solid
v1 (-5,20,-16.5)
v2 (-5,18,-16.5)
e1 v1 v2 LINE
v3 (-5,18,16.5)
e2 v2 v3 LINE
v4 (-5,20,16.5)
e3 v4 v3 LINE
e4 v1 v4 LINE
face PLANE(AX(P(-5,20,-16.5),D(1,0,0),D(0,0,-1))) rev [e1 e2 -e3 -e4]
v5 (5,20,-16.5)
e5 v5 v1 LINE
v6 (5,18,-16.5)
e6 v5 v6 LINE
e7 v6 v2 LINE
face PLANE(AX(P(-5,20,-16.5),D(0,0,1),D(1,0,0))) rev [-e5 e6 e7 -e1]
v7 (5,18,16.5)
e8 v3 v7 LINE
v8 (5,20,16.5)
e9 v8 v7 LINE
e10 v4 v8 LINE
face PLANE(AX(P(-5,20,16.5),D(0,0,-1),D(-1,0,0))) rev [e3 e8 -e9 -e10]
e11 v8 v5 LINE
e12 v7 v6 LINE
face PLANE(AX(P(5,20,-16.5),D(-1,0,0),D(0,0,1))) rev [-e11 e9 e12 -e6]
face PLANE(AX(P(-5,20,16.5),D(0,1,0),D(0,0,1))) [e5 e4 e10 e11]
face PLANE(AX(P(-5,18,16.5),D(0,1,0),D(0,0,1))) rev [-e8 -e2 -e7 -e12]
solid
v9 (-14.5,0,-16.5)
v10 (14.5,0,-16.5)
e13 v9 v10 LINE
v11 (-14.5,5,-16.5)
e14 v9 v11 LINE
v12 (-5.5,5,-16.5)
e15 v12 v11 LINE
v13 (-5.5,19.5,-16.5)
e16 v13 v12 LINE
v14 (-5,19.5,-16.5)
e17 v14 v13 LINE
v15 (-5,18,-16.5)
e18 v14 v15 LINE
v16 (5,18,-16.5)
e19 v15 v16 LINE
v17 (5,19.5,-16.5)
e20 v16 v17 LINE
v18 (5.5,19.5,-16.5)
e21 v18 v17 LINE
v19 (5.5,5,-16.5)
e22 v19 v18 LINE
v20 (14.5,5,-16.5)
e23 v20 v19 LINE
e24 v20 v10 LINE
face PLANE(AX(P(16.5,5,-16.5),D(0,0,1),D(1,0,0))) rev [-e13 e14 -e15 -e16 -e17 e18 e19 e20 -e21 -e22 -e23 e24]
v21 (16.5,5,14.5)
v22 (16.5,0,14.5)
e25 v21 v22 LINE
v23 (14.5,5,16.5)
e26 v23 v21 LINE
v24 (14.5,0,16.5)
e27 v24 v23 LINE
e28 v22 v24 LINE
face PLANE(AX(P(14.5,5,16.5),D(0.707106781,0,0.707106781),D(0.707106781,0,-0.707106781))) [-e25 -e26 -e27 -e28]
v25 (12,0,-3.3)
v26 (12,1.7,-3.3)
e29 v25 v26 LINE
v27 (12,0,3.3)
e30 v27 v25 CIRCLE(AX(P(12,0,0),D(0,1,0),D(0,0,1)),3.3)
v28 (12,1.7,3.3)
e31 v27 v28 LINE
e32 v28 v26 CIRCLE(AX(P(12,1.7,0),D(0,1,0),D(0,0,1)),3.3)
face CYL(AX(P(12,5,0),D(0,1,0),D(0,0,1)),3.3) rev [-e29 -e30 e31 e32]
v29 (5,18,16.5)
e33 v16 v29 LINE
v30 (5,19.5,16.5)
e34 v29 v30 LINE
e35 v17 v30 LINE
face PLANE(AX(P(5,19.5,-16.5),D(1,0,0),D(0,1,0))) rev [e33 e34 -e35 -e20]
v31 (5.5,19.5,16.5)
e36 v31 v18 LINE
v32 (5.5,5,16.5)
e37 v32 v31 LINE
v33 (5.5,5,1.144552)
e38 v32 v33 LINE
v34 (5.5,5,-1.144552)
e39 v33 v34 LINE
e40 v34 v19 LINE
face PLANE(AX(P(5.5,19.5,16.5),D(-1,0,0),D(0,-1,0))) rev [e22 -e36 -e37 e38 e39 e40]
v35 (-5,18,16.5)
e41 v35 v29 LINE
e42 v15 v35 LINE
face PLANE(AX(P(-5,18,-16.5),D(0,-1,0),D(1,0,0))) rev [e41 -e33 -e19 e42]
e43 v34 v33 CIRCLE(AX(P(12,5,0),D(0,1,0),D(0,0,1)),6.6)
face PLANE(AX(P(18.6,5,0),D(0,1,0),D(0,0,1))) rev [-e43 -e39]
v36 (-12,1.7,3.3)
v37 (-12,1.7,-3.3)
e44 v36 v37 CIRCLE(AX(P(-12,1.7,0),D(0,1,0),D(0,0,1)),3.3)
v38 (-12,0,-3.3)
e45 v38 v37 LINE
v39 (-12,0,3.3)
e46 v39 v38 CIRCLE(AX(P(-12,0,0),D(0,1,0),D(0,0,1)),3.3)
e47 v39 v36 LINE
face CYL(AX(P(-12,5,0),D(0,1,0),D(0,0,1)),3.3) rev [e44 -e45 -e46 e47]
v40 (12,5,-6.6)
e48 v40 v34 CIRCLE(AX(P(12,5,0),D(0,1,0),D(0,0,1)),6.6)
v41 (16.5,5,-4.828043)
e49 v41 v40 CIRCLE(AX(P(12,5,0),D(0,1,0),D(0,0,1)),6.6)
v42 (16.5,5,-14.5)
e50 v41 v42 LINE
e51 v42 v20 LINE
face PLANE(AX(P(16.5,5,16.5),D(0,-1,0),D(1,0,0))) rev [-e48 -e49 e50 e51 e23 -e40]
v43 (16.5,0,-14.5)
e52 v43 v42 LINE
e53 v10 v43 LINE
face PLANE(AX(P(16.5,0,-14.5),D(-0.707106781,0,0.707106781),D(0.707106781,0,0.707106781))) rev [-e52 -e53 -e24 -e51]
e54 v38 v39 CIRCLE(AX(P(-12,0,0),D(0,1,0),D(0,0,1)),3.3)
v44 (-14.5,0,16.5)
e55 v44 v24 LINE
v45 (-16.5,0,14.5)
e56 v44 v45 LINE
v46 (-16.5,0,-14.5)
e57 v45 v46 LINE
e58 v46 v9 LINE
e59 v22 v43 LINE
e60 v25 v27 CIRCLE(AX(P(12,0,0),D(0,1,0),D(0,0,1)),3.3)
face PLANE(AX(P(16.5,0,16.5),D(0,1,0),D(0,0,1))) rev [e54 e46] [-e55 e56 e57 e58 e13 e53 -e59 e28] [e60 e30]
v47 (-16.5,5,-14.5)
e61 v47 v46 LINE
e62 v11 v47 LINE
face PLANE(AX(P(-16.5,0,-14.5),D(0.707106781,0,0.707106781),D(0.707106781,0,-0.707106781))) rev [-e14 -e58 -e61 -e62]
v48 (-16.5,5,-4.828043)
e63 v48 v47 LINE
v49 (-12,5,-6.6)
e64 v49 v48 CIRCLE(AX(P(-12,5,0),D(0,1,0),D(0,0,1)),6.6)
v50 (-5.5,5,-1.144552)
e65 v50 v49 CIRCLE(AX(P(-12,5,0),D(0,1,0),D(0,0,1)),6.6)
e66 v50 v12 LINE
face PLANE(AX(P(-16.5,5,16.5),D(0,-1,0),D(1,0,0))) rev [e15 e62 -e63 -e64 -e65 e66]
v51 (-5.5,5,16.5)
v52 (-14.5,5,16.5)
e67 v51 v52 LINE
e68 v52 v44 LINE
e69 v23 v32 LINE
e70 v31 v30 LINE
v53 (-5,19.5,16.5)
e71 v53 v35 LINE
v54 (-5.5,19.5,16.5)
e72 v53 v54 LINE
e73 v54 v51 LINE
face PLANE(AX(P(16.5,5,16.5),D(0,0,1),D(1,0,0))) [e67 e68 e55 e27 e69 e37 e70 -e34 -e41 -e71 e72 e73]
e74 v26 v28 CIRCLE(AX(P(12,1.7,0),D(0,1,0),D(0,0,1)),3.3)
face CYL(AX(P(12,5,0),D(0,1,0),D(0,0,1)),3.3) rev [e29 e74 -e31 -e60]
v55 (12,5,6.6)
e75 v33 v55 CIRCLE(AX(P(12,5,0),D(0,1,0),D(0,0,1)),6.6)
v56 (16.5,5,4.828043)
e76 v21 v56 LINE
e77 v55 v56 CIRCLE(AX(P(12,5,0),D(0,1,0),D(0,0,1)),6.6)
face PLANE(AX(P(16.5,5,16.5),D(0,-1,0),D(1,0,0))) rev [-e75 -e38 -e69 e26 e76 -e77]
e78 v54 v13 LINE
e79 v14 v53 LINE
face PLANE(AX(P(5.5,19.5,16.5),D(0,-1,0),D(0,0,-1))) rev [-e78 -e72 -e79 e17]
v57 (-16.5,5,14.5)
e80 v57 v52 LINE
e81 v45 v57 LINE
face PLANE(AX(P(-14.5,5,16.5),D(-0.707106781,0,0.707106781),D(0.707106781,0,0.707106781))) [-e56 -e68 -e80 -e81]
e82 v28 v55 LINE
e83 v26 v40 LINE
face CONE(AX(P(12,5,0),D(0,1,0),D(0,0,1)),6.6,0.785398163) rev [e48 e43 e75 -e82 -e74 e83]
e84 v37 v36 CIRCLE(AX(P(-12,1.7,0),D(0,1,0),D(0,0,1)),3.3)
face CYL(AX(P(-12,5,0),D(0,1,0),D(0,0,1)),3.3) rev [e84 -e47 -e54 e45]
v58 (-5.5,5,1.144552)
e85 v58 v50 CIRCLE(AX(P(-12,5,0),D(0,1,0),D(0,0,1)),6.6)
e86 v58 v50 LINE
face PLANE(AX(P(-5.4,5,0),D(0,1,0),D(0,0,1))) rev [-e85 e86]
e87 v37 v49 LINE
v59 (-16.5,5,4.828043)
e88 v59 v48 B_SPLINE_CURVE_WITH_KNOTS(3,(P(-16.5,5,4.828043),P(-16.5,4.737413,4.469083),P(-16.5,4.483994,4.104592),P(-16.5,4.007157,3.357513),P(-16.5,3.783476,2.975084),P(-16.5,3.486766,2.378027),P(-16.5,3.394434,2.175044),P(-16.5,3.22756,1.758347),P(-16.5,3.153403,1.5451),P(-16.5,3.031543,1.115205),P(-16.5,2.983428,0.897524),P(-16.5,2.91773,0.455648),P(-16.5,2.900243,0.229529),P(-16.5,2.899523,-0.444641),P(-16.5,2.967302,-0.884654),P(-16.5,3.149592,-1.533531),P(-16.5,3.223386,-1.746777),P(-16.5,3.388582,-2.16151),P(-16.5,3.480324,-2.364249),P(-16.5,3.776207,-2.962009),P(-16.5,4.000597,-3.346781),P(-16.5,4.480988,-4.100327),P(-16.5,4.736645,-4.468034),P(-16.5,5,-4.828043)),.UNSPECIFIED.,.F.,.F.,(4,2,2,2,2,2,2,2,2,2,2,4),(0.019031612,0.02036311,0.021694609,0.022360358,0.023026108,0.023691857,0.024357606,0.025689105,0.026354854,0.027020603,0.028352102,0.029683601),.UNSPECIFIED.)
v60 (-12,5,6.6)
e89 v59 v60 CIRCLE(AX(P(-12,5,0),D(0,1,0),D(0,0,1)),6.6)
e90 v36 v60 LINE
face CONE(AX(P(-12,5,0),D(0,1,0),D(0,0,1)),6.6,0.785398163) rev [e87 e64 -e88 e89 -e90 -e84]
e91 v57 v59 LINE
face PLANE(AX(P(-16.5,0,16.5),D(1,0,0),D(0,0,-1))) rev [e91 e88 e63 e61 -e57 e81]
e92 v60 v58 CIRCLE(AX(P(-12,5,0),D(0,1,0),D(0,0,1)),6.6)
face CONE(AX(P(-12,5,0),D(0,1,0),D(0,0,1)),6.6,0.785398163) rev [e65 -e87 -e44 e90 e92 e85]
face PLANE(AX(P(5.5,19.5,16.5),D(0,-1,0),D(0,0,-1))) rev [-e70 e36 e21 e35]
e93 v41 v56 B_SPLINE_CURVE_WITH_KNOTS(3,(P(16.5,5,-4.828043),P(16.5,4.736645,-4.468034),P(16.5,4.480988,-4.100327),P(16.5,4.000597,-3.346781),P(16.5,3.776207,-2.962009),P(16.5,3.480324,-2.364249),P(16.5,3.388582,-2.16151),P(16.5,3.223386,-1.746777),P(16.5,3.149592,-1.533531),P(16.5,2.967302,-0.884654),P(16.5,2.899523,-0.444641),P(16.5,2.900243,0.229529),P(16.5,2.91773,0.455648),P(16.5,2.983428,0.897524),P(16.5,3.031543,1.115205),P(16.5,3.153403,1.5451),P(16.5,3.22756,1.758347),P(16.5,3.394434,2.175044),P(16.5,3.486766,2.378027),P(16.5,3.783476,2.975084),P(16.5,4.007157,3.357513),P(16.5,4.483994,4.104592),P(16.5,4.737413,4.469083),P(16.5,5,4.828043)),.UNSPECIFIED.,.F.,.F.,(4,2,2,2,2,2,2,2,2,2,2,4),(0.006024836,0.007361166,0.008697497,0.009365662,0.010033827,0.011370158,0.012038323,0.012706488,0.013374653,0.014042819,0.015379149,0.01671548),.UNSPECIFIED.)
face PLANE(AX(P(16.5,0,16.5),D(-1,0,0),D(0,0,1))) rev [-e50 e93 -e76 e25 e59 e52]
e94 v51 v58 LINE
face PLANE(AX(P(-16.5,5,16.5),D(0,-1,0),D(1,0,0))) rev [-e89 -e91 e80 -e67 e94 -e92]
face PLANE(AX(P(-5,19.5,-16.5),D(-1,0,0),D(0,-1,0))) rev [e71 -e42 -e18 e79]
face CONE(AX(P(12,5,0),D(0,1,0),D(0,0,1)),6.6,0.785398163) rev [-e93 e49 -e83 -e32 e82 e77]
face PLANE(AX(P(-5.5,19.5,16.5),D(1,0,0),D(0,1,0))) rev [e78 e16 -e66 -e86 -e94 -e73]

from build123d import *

# Parameters (mm, degrees)
BOSS_EXTRUDE1_DEPTH                          = 16.5
SKETCH2_W                                    = 10
SKETCH2_H                                    = 1.5
CUT_EXTRUDE1_DEPTH                           = 42.73128323
SKETCH3_W                                    = 10
SKETCH3_H                                    = 33
BOSS_EXTRUDE2_DEPTH                          = 2
HOLE_SIZE_PER_CROSS_RECESS_WOOD_SCRE_2_COUNT = 2
HOLE_SIZE_PER_CROSS_RECESS_WOOD_SCRE_2_PITCH = 24
CHAMFER1_SIZE                                = 2


with BuildPart() as part:
    # Sketch1 → Boss-Extrude1 (new, symmetric)
    with BuildSketch(Plane.XY):
        Polygon((16.5, 0), (-16.5, 0), (-16.5, 5), (-5.5, 5), (-5.5, 19.5), (5.5, 19.5), (5.5, 5), (16.5, 5), align=None)
    extrude(amount=BOSS_EXTRUDE1_DEPTH, both=True)

    # Sketch2 → Cut-Extrude1 (cut, through all)
    with BuildSketch(Plane.XY.offset(16.5)):
        with Locations((0, 18.75)):
            Rectangle(SKETCH2_W, SKETCH2_H)
    extrude(amount=-CUT_EXTRUDE1_DEPTH, mode=Mode.SUBTRACT)

    # Sketch4 → Hole size per cross recess wood screw type 1 (revolve, cut)
    with BuildSketch(Plane(origin=(-12, 5, 0), x_dir=(0, 0, 1), z_dir=(1, 0, 0))):
        Polygon((0, 0), (0, 5), (3.3, 5), (3.3, 3.3), (6.6, 0), align=None)
    hole_size_per_cross_recess_wood_screw_ty = revolve(axis=Axis((-12, 11.35, 0), (0, -1, 0)), mode=Mode.SUBTRACT)

    # Hole size per cross recess wood scre 2: Hole size per cross recess wood screw type 1 ×2
    with Locations(*[(i * HOLE_SIZE_PER_CROSS_RECESS_WOOD_SCRE_2_PITCH, 0, 0) for i in range(1, HOLE_SIZE_PER_CROSS_RECESS_WOOD_SCRE_2_COUNT)]):
        add(hole_size_per_cross_recess_wood_screw_ty, mode=Mode.SUBTRACT)

    # Chamfer1
    chamfer1_edges = [part.edges().sort_by_distance(p)[0] for p in [
        (16.5, 2.5, -16.5),
        (-16.5, 2.5, 16.5),
        (16.5, 2.5, 16.5),
        (-16.5, 2.5, -16.5),
    ]]
    chamfer(chamfer1_edges, length=CHAMFER1_SIZE)


with BuildPart() as body_2:
    # Sketch3 → Boss-Extrude2 (new body)
    with BuildSketch(Plane(origin=(0, 18, 0), x_dir=(1, 0, 0), z_dir=(0, 1, 0))):
        Rectangle(SKETCH3_W, SKETCH3_H)
    extrude(amount=BOSS_EXTRUDE2_DEPTH)


solid = Compound([part.part, body_2.part])
